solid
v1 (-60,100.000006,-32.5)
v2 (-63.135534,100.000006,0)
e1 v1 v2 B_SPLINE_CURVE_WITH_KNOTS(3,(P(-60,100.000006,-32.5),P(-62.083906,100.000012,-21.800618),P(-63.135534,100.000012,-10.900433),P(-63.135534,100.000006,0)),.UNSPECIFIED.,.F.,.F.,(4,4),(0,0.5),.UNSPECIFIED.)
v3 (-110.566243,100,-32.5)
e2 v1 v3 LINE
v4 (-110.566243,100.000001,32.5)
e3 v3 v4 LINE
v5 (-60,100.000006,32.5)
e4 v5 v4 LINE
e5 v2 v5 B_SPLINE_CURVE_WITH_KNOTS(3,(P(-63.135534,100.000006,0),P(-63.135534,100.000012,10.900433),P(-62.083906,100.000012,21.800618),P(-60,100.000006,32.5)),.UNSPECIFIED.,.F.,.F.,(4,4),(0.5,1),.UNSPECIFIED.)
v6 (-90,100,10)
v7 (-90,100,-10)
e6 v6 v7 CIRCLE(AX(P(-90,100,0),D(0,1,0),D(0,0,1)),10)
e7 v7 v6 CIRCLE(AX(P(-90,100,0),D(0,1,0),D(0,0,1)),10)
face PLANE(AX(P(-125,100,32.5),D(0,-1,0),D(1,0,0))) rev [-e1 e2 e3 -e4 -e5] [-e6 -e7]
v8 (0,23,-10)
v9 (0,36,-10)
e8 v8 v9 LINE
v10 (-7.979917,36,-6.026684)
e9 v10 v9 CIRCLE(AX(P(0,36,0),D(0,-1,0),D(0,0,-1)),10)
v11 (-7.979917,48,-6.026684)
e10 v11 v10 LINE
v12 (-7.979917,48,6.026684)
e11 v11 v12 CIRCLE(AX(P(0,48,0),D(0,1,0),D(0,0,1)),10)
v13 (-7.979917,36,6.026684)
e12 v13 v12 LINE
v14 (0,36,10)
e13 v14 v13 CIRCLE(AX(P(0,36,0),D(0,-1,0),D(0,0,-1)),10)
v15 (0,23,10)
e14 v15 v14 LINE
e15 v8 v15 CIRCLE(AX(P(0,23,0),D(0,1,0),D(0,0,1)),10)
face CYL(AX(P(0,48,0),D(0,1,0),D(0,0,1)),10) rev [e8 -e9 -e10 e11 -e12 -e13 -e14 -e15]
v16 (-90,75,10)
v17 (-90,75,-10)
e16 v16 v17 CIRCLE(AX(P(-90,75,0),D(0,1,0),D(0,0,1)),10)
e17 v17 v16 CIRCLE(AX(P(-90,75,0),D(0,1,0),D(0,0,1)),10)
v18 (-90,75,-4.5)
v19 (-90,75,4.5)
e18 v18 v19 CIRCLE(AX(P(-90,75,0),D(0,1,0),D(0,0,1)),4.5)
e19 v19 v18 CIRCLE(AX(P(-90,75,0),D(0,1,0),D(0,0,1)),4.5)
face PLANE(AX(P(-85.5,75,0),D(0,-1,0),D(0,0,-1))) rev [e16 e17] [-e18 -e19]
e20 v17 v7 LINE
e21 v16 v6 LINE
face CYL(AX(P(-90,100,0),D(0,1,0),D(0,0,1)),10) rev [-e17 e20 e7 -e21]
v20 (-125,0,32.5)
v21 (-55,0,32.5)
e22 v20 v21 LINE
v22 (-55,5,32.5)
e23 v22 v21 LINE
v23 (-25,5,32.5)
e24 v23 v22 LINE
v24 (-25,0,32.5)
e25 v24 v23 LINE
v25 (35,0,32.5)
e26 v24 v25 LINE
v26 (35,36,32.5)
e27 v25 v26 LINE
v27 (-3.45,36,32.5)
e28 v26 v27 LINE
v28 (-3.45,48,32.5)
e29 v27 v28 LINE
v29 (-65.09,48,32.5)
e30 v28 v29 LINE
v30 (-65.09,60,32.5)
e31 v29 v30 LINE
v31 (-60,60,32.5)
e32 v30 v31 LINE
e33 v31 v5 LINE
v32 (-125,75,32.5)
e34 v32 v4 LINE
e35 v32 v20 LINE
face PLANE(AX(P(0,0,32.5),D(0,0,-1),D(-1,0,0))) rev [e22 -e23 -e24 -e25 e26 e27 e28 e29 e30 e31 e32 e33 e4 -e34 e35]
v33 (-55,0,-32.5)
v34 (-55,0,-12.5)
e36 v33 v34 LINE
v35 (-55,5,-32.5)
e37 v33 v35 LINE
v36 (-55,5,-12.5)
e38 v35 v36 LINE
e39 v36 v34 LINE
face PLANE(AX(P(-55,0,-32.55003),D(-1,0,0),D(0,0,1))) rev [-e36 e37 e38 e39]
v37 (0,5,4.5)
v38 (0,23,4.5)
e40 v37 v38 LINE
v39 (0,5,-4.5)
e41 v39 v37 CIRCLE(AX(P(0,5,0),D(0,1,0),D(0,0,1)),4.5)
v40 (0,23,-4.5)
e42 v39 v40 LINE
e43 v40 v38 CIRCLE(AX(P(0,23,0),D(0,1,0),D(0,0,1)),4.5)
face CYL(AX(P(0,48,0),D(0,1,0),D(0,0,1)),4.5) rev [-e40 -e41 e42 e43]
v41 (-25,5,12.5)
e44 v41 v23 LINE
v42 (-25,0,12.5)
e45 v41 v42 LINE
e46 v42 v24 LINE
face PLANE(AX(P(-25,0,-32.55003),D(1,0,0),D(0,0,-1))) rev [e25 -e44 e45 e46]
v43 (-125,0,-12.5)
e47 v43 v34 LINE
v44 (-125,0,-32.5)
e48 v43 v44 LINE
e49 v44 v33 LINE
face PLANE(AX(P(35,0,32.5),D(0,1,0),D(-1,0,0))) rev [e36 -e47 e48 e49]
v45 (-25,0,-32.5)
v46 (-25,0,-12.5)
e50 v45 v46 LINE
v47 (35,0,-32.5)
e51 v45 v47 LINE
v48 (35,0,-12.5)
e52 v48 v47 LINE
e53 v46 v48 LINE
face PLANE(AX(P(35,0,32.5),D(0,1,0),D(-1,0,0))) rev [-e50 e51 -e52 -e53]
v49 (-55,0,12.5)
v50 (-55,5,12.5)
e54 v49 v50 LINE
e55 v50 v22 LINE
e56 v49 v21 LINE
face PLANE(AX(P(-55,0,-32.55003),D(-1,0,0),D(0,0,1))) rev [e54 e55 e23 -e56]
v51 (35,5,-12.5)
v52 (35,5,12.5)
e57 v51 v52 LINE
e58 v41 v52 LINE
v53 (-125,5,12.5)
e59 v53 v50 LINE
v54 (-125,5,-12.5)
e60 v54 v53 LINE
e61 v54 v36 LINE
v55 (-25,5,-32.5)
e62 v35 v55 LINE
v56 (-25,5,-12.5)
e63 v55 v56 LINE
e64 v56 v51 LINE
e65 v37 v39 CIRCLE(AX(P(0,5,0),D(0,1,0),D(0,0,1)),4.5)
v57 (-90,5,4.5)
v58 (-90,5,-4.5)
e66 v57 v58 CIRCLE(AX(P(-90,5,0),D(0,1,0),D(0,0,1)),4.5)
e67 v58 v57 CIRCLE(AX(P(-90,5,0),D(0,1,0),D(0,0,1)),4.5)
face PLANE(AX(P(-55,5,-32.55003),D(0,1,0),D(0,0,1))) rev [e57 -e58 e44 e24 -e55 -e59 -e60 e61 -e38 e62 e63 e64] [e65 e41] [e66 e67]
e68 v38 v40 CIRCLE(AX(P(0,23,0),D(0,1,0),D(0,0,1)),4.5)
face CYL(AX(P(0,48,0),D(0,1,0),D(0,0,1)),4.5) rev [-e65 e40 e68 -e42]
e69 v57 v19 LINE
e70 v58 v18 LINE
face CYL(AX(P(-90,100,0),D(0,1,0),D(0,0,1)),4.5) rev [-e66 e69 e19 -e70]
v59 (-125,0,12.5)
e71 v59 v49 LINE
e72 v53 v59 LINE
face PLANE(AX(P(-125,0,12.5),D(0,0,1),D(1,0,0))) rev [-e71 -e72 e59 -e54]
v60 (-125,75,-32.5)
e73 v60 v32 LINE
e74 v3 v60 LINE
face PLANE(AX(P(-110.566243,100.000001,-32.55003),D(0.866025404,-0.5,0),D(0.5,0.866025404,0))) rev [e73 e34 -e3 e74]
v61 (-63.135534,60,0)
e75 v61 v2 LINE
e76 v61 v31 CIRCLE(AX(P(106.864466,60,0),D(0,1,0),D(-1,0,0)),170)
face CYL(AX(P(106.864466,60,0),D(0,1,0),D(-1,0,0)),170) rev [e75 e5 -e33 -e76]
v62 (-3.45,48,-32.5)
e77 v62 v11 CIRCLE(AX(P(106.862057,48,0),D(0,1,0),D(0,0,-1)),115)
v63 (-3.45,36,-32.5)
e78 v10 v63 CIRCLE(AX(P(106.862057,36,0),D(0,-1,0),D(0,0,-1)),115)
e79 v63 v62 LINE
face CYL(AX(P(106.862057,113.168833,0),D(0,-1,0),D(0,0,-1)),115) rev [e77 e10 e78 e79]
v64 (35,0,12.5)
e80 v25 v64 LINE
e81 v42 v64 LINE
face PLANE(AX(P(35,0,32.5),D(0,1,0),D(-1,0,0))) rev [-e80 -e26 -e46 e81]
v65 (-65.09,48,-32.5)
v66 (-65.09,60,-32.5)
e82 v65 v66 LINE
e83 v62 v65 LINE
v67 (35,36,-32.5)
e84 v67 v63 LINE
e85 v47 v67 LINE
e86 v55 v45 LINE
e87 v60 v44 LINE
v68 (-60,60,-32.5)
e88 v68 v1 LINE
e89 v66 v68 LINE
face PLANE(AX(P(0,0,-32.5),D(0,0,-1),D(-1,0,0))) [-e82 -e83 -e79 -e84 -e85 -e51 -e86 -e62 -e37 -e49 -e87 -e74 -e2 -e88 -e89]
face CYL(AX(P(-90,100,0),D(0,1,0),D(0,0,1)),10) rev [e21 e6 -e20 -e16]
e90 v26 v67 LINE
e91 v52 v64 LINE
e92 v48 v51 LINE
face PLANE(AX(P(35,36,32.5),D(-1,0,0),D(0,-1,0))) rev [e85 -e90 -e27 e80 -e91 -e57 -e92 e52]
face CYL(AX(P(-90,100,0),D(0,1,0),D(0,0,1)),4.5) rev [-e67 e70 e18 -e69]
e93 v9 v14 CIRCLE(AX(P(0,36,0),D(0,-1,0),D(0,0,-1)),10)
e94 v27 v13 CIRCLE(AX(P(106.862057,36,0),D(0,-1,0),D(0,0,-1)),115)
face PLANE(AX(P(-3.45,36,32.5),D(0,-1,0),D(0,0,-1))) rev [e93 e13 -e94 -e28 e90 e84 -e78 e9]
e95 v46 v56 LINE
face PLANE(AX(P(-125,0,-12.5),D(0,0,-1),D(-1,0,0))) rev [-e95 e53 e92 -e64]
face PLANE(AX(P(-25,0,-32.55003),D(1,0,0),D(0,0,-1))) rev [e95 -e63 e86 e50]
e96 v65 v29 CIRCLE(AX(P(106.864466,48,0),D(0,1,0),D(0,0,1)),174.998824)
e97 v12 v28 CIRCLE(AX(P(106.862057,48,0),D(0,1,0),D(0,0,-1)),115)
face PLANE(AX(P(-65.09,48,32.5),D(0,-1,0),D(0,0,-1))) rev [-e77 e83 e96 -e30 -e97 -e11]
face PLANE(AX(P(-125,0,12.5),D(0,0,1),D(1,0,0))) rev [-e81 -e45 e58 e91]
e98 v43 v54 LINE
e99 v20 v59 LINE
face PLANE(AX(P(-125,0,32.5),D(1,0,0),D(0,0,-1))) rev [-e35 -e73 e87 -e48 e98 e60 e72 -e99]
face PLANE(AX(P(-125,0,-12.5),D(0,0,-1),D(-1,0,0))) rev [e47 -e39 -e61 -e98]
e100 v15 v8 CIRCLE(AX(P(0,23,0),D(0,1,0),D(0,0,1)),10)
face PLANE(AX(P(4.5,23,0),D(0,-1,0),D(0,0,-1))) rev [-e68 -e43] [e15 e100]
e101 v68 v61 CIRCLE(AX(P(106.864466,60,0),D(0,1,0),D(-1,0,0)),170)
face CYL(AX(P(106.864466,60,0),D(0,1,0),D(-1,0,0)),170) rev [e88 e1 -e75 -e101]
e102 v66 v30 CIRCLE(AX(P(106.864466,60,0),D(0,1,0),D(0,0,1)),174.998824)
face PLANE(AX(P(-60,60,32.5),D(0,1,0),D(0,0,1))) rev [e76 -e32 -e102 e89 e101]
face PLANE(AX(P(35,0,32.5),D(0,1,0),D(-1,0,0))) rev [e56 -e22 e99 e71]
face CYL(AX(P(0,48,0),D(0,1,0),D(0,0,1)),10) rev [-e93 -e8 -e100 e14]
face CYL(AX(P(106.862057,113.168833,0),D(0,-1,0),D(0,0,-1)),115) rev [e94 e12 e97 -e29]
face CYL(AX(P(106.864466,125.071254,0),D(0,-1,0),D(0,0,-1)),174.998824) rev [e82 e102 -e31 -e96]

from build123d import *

# Parameters (mm, degrees)
BRACKET_BODY_DEPTH                   = 32.5
TOP_CURVED_SEAT_CUT_R170_DEPTH       = 164.343962239
TOP_CURVED_SEAT_CUT_R170_DEPTH_BACK  = 40
STEP_CURVED_SEAT_CUT_R175_DEPTH      = 12
CURVED_RELIEF_CUT_R115_DEPTH         = 12
CORNER_CHAMFER_CUT_25X30DEG_DEPTH    = 173.771525432
UNDERSIDE_GROOVE_SKETCH_60X30_W      = 30
UNDERSIDE_GROOVE_SKETCH_60X30_H      = 5
UNDERSIDE_GROOVE_60X30X5_DEPTH       = 173.771525432
UNDERSIDE_NOTCH_SKETCH_20X20_W       = 25
UNDERSIDE_NOTCH_SKETCH_20X20_H       = 5
UNDERSIDE_NOTCH_20X20X5_DEPTH        = 192.458219985
C_BORE_HOLE_9_LOW_STEP_D             = 9
C_BORE_HOLE_9_LOW_STEP_CBORE_D       = 20
C_BORE_HOLE_9_LOW_STEP_CBORE_DEPTH   = 25
C_BORE_HOLE_9_HIGH_BLOCK_D           = 9
C_BORE_HOLE_9_HIGH_BLOCK_CBORE_D     = 20
C_BORE_HOLE_9_HIGH_BLOCK_CBORE_DEPTH = 25


with BuildPart() as part:
    # Bracket Side Profile Sketch → Bracket Body (new, symmetric)
    with BuildSketch(Plane.XY):
        Polygon((35, 0), (-125, 0), (-125, 100), (-60, 100), (-60, 60), (-65.09, 60), (-65.09, 48), (-3.45, 48), (-3.45, 36), (35, 36), align=None)
    extrude(amount=BRACKET_BODY_DEPTH, both=True)

    # Top Curved Seat Sketch R170 → Top Curved Seat Cut R170 (cut, two sides: drawn at the far end of the back side and taken through both)
    with BuildSketch(Plane(origin=(0, 100, 0), x_dir=(1, 0, 0), z_dir=(0, 1, 0)).offset(-TOP_CURVED_SEAT_CUT_R170_DEPTH_BACK)):
        with BuildLine():
            ThreePointArc((-60, 32.5), (-63.13553404, 0), (-60, -32.5))
            Line((-60, -32.5), (-60, 32.5))
        make_face()
    extrude(amount=TOP_CURVED_SEAT_CUT_R170_DEPTH + TOP_CURVED_SEAT_CUT_R170_DEPTH_BACK, mode=Mode.SUBTRACT)

    # Step Curved Seat Sketch R175 → Step Curved Seat Cut R175 (cut)
    with BuildSketch(Plane(origin=(0, 48, 0), x_dir=(1, 0, 0), z_dir=(0, 1, 0))):
        with BuildLine():
            ThreePointArc((-65.09, 32.5), (-68.134357932, 0), (-65.09, -32.5))
            Line((-65.09, -32.5), (-65.09, 32.5))
        make_face()
    extrude(amount=STEP_CURVED_SEAT_CUT_R175_DEPTH, mode=Mode.SUBTRACT)

    # Curved Relief Sketch R115 → Curved Relief Cut R115 (cut)
    with BuildSketch(Plane(origin=(0, 36, 0), x_dir=(1, 0, 0), z_dir=(0, 1, 0))):
        with BuildLine():
            Line((-3.45, -32.5), (-3.45, 32.5))
            ThreePointArc((-3.45, 32.5), (-8.137942635, 0), (-3.45, -32.5))
        make_face()
    extrude(amount=CURVED_RELIEF_CUT_R115_DEPTH, mode=Mode.SUBTRACT)

    # Corner Chamfer Sketch 25x30deg → Corner Chamfer Cut 25x30deg (cut, through all)
    with BuildSketch(Plane.XY.offset(32.5)):
        Polygon((-125, 100), (-110.566242501, 100.000001332), (-125, 75), align=None)
    extrude(amount=-CORNER_CHAMFER_CUT_25X30DEG_DEPTH, mode=Mode.SUBTRACT)

    # Underside Groove Sketch 60x30 → Underside Groove 60x30x5 (cut, through all)
    with BuildSketch(Plane.XY.offset(32.5)):
        with Locations((-40, 2.5)):
            Rectangle(UNDERSIDE_GROOVE_SKETCH_60X30_W, UNDERSIDE_GROOVE_SKETCH_60X30_H)
    extrude(amount=-UNDERSIDE_GROOVE_60X30X5_DEPTH, mode=Mode.SUBTRACT)

    # Underside Notch Sketch 20x20 → Underside Notch 20x20x5 (cut, through all)
    with BuildSketch(Plane(origin=(35, 0, 0), x_dir=(0, 0, -1), z_dir=(1, 0, 0))):
        with Locations((0, 2.5)):
            Rectangle(UNDERSIDE_NOTCH_SKETCH_20X20_W, UNDERSIDE_NOTCH_SKETCH_20X20_H)
    extrude(amount=-UNDERSIDE_NOTCH_20X20X5_DEPTH, mode=Mode.SUBTRACT)

    # C-Bore Hole Ø9 Low Step (through all)
    with Locations(Plane(origin=(0, 48, 0), x_dir=(1, 0, 0), z_dir=(0, 1, 0))):
        with Locations((0, 0)):
            CounterBoreHole(C_BORE_HOLE_9_LOW_STEP_D / 2, C_BORE_HOLE_9_LOW_STEP_CBORE_D / 2, C_BORE_HOLE_9_LOW_STEP_CBORE_DEPTH)

    # C-Bore Hole Ø9 High Block (through all)
    with Locations(Plane(origin=(0, 100, 0), x_dir=(1, 0, 0), z_dir=(0, 1, 0))):
        with Locations((-90, 0)):
            CounterBoreHole(C_BORE_HOLE_9_HIGH_BLOCK_D / 2, C_BORE_HOLE_9_HIGH_BLOCK_CBORE_D / 2, C_BORE_HOLE_9_HIGH_BLOCK_CBORE_DEPTH)


solid = part.part
